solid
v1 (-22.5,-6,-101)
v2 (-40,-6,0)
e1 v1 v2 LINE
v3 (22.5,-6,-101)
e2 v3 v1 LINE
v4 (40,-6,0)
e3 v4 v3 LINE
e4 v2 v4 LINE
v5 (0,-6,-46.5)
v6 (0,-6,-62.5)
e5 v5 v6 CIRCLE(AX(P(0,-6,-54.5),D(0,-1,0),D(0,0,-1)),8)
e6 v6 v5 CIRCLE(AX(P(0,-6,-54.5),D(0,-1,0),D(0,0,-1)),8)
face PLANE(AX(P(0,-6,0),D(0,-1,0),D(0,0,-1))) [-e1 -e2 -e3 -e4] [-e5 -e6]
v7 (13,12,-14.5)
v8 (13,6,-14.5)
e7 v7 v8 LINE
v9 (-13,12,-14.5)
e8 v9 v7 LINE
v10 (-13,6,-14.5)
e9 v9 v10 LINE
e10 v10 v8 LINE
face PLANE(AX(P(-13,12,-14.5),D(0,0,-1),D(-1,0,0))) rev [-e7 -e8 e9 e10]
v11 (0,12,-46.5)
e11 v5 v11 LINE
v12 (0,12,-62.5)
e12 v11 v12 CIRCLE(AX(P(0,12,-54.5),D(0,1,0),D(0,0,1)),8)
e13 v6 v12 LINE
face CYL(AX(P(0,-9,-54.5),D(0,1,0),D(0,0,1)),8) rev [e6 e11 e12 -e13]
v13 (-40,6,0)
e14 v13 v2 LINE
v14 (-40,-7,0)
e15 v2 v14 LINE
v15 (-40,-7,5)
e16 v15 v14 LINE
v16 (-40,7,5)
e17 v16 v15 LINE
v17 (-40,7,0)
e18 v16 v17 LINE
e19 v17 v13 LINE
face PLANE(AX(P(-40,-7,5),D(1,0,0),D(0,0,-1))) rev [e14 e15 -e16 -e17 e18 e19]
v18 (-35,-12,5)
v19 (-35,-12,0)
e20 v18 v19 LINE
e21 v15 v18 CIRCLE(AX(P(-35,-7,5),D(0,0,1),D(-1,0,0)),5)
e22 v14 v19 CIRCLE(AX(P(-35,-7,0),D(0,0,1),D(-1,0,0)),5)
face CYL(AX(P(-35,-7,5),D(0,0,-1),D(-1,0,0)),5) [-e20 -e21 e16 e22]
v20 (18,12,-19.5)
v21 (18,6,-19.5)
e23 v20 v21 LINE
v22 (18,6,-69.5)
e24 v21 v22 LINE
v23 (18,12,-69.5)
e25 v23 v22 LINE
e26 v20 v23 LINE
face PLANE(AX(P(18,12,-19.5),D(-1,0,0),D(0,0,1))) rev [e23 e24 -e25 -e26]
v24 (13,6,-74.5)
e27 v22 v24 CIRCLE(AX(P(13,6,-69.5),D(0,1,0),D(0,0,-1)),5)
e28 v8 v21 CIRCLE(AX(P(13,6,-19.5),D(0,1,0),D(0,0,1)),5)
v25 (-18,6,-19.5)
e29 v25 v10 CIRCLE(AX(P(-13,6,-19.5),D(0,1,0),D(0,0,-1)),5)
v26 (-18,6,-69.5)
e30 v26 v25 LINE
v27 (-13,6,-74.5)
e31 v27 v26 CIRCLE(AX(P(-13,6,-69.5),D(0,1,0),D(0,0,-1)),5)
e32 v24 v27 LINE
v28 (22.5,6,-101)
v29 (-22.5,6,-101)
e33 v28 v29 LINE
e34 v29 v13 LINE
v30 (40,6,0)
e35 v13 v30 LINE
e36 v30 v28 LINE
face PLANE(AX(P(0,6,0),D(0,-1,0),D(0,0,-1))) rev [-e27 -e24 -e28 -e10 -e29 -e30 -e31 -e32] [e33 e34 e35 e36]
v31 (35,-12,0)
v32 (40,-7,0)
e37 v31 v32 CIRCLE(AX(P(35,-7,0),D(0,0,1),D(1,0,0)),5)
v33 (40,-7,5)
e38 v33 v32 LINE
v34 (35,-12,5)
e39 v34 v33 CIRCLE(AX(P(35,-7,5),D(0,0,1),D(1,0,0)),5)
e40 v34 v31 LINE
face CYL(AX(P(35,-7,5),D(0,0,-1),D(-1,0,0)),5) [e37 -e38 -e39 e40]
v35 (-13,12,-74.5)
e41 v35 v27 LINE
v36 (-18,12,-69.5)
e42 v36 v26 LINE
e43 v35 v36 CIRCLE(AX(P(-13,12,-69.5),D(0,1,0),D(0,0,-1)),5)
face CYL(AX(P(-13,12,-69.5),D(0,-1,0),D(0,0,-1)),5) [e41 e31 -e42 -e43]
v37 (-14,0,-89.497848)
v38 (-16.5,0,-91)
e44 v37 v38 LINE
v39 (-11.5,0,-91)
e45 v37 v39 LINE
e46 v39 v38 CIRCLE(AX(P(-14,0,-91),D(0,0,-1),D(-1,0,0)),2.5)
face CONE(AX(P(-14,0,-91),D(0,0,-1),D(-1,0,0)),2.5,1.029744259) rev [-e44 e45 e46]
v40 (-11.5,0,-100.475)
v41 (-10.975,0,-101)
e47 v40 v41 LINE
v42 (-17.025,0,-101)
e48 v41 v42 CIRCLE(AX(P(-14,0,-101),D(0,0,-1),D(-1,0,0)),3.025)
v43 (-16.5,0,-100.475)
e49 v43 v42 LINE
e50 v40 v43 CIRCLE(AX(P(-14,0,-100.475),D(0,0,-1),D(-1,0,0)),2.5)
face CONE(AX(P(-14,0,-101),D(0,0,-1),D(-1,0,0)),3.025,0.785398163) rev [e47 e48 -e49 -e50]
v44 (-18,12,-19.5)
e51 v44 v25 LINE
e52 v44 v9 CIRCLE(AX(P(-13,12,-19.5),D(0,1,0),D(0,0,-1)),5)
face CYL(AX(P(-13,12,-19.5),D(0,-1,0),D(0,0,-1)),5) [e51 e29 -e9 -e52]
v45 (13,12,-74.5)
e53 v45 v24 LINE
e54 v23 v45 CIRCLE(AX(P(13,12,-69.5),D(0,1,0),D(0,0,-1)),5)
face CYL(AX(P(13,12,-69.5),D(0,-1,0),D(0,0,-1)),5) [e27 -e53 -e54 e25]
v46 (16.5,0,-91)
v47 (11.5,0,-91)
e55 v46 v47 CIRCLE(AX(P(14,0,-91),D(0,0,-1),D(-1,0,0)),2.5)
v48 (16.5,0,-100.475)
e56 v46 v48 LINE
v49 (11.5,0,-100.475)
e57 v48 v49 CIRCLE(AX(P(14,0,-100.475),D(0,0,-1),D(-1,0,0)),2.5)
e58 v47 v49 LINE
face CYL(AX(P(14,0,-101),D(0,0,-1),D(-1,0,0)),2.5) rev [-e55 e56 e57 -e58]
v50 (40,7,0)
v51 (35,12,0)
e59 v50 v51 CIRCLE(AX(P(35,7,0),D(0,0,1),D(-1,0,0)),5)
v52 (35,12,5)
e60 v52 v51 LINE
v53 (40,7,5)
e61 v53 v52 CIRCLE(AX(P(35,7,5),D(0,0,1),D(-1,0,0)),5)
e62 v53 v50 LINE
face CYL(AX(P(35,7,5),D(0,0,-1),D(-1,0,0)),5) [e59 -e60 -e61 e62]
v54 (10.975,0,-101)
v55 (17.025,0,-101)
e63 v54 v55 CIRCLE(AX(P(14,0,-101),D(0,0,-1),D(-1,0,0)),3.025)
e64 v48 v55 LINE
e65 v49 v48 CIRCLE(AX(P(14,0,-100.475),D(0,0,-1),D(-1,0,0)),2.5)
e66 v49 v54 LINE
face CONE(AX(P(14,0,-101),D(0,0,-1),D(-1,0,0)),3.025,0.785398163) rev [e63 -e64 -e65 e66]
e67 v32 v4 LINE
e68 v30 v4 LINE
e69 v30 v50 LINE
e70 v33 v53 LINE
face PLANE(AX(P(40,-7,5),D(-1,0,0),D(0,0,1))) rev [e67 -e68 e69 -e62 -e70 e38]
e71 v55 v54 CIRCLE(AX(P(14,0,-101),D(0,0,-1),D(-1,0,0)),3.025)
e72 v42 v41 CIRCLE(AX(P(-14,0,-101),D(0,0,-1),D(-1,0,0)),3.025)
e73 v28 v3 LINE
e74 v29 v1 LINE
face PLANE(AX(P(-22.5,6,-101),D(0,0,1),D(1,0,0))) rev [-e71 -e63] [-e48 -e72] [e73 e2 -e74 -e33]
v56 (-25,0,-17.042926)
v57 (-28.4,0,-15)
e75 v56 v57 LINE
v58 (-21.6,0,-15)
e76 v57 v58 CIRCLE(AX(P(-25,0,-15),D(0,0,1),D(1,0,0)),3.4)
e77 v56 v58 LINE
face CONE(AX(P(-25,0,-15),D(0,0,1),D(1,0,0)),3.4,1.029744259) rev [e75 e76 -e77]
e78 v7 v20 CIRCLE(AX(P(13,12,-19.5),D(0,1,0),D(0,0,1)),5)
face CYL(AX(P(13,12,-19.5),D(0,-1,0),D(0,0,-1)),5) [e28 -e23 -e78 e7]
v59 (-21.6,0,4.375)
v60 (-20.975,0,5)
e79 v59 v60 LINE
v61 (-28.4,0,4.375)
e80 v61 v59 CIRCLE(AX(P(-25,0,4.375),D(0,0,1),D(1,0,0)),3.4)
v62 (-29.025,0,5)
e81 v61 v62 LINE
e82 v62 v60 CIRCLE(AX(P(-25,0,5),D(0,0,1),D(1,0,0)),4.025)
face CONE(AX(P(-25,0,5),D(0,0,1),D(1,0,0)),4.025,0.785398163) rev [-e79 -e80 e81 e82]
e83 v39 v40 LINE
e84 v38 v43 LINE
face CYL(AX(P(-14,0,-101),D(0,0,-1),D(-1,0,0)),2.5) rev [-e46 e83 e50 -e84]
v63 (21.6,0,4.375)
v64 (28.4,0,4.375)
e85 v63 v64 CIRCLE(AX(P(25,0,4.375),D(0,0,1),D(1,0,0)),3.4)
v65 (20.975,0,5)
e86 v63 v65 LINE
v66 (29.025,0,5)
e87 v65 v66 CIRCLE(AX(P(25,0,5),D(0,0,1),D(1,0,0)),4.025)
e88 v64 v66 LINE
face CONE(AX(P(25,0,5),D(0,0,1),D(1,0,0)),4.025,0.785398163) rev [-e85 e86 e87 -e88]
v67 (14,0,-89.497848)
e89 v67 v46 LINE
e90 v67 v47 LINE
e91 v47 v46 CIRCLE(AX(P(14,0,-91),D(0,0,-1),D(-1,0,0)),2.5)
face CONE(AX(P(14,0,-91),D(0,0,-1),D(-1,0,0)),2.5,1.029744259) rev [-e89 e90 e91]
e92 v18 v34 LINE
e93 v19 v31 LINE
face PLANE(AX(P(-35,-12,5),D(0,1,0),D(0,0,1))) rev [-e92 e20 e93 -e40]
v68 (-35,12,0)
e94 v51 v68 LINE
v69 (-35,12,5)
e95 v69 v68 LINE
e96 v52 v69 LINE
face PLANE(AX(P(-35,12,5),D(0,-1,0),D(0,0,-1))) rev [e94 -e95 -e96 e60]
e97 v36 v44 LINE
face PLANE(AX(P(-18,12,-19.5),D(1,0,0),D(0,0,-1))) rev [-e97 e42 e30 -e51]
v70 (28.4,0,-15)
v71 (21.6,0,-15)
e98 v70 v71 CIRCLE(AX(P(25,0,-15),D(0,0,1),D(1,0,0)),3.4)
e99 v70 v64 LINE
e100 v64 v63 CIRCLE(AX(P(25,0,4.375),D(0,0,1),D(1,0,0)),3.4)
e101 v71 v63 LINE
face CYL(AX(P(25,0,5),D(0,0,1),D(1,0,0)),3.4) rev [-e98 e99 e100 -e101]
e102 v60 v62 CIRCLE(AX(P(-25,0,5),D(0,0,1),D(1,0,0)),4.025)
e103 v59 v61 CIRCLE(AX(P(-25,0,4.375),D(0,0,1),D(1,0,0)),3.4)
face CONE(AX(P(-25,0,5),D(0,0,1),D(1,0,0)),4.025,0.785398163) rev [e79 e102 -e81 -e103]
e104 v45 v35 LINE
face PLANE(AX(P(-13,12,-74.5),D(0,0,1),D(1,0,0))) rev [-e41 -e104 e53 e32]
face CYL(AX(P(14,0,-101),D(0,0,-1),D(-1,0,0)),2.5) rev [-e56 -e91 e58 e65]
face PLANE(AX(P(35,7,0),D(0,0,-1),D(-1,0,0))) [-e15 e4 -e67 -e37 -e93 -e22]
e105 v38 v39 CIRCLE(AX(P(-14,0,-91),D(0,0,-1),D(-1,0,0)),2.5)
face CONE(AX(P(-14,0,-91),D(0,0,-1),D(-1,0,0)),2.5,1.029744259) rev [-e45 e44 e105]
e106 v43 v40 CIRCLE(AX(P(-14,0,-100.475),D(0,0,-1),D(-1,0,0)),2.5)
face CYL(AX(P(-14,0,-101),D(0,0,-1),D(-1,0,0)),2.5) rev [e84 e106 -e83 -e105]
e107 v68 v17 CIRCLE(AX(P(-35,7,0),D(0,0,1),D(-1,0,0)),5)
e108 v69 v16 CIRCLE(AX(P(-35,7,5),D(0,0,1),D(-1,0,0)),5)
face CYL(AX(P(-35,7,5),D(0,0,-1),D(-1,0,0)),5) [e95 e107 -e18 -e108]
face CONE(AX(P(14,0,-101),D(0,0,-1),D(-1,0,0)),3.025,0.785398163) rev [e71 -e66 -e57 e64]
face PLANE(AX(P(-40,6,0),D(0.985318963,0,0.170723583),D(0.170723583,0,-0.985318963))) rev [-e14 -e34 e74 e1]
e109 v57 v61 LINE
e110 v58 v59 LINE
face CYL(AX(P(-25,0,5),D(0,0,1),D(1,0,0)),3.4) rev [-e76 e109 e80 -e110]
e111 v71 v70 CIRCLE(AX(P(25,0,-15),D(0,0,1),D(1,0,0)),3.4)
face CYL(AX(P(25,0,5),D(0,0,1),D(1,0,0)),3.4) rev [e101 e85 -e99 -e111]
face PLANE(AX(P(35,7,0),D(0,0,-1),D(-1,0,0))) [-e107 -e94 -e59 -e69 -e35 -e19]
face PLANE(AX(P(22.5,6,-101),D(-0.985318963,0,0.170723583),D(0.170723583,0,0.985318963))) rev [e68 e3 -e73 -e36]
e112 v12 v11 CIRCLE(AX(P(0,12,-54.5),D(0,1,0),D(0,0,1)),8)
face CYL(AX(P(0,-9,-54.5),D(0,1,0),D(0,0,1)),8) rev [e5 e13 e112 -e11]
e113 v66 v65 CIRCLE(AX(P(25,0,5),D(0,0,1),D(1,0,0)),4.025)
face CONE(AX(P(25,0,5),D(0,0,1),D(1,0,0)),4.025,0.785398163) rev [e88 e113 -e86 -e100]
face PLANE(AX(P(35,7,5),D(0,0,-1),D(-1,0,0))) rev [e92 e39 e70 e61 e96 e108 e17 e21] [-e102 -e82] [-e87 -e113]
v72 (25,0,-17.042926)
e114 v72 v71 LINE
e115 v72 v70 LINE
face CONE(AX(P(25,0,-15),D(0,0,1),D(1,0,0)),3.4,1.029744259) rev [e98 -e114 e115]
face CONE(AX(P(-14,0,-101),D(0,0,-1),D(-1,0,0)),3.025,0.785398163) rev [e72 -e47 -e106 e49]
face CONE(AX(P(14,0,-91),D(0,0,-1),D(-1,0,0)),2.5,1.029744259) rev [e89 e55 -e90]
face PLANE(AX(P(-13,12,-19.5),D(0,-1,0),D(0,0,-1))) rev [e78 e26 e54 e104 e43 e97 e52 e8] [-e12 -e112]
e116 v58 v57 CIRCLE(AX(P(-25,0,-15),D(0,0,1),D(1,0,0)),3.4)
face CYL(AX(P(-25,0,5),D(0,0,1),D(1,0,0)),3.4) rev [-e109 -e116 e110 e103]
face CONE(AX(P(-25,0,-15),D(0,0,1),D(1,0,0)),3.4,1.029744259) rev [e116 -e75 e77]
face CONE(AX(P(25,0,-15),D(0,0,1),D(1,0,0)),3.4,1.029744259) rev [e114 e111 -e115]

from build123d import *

# Parameters (mm, degrees)
BOSS_EXTRUDE1_DEPTH         = 5
BOSS_EXTRUDE2_DEPTH         = 6
BOSS_EXTRUDE3_DEPTH         = 6
SKETCH4_R                   = 8
CUT_EXTRUDE1_DEPTH          = 21
M8_TAPPED_HOLE1_D           = 6.8
M8_TAPPED_HOLE1_DEPTH       = 20
M8_TAPPED_HOLE1_CSINK_D     = 8.05
M8_TAPPED_HOLE1_CSINK_ANGLE = 90
M8_TAPPED_HOLE1_TIP         = 2.042926105
M6_TAPPED_HOLE1_D           = 5
M6_TAPPED_HOLE1_DEPTH       = 10
M6_TAPPED_HOLE1_CSINK_D     = 6.05
M6_TAPPED_HOLE1_CSINK_ANGLE = 90
M6_TAPPED_HOLE1_TIP         = 1.502151548


with BuildPart() as part:
    # Sketch1 → Boss-Extrude1 (new body)
    with BuildSketch(Plane.XY):
        with BuildLine():
            Line((-35, -12), (35, -12))
            ThreePointArc((35, -12), (38.535533906, -10.535533906), (40, -7))
            Line((40, -7), (40, 7))
            ThreePointArc((40, 7), (38.535533906, 10.535533906), (35, 12))
            Line((35, 12), (-35, 12))
            ThreePointArc((-35, 12), (-38.535533906, 10.535533906), (-40, 7))
            Line((-40, 7), (-40, -7))
            ThreePointArc((-40, -7), (-38.535533906, -10.535533906), (-35, -12))
        make_face()
    extrude(amount=BOSS_EXTRUDE1_DEPTH)

    # Sketch2 → Boss-Extrude2 (add, symmetric)
    with BuildSketch(Plane(origin=(0, 0, 0), x_dir=(1, 0, 0), z_dir=(0, 1, 0))):
        Polygon((-40, 0), (-22.5, 101), (22.5, 101), (40, 0), align=None)
    extrude(amount=BOSS_EXTRUDE2_DEPTH, both=True)

    # Sketch3 → Boss-Extrude3 (add)
    with BuildSketch(Plane(origin=(0, 6, 0), x_dir=(1, 0, 0), z_dir=(0, 1, 0))):
        with BuildLine():
            Line((-13, 14.5), (13, 14.5))
            ThreePointArc((13, 14.5), (16.535533906, 15.964466094), (18, 19.5))
            Line((18, 19.5), (18, 69.5))
            ThreePointArc((18, 69.5), (16.535533906, 73.035533906), (13, 74.5))
            Line((13, 74.5), (-13, 74.5))
            ThreePointArc((-13, 74.5), (-16.535533906, 73.035533906), (-18, 69.5))
            Line((-18, 69.5), (-18, 19.5))
            ThreePointArc((-18, 19.5), (-16.535533906, 15.964466094), (-13, 14.5))
        make_face()
    extrude(amount=BOSS_EXTRUDE3_DEPTH)

    # Sketch4 → Cut-Extrude1 (cut)
    with BuildSketch(Plane(origin=(0, 12, 0), x_dir=(1, 0, 0), z_dir=(0, 1, 0))):
        with Locations(Location((0, 54.5, 0), (0, 0, 270))):
            Circle(SKETCH4_R)
    extrude(amount=-CUT_EXTRUDE1_DEPTH, mode=Mode.SUBTRACT)

    # M8 Tapped Hole1
    with Locations(Plane(origin=(25, 0, 5), x_dir=(1, 0, 0), z_dir=(0, 0, 1))):
        with Locations((0, 0), (-50, 0)):
            CounterSinkHole(M8_TAPPED_HOLE1_D / 2, M8_TAPPED_HOLE1_CSINK_D / 2, depth=M8_TAPPED_HOLE1_DEPTH, counter_sink_angle=M8_TAPPED_HOLE1_CSINK_ANGLE)
            with Locations((0, 0, -(M8_TAPPED_HOLE1_DEPTH + M8_TAPPED_HOLE1_TIP / 2))):  # 118° drill point
                Cone(0, M8_TAPPED_HOLE1_D / 2, M8_TAPPED_HOLE1_TIP, mode=Mode.SUBTRACT)

    # M6 Tapped Hole1
    with Locations(Plane(origin=(14, 0, -101), x_dir=(-1, 0, 0), z_dir=(0, 0, -1))):
        with Locations((0, 0), (28, 0)):
            CounterSinkHole(M6_TAPPED_HOLE1_D / 2, M6_TAPPED_HOLE1_CSINK_D / 2, depth=M6_TAPPED_HOLE1_DEPTH, counter_sink_angle=M6_TAPPED_HOLE1_CSINK_ANGLE)
            with Locations((0, 0, -(M6_TAPPED_HOLE1_DEPTH + M6_TAPPED_HOLE1_TIP / 2))):  # 118° drill point
                Cone(0, M6_TAPPED_HOLE1_D / 2, M6_TAPPED_HOLE1_TIP, mode=Mode.SUBTRACT)


solid = part.part
